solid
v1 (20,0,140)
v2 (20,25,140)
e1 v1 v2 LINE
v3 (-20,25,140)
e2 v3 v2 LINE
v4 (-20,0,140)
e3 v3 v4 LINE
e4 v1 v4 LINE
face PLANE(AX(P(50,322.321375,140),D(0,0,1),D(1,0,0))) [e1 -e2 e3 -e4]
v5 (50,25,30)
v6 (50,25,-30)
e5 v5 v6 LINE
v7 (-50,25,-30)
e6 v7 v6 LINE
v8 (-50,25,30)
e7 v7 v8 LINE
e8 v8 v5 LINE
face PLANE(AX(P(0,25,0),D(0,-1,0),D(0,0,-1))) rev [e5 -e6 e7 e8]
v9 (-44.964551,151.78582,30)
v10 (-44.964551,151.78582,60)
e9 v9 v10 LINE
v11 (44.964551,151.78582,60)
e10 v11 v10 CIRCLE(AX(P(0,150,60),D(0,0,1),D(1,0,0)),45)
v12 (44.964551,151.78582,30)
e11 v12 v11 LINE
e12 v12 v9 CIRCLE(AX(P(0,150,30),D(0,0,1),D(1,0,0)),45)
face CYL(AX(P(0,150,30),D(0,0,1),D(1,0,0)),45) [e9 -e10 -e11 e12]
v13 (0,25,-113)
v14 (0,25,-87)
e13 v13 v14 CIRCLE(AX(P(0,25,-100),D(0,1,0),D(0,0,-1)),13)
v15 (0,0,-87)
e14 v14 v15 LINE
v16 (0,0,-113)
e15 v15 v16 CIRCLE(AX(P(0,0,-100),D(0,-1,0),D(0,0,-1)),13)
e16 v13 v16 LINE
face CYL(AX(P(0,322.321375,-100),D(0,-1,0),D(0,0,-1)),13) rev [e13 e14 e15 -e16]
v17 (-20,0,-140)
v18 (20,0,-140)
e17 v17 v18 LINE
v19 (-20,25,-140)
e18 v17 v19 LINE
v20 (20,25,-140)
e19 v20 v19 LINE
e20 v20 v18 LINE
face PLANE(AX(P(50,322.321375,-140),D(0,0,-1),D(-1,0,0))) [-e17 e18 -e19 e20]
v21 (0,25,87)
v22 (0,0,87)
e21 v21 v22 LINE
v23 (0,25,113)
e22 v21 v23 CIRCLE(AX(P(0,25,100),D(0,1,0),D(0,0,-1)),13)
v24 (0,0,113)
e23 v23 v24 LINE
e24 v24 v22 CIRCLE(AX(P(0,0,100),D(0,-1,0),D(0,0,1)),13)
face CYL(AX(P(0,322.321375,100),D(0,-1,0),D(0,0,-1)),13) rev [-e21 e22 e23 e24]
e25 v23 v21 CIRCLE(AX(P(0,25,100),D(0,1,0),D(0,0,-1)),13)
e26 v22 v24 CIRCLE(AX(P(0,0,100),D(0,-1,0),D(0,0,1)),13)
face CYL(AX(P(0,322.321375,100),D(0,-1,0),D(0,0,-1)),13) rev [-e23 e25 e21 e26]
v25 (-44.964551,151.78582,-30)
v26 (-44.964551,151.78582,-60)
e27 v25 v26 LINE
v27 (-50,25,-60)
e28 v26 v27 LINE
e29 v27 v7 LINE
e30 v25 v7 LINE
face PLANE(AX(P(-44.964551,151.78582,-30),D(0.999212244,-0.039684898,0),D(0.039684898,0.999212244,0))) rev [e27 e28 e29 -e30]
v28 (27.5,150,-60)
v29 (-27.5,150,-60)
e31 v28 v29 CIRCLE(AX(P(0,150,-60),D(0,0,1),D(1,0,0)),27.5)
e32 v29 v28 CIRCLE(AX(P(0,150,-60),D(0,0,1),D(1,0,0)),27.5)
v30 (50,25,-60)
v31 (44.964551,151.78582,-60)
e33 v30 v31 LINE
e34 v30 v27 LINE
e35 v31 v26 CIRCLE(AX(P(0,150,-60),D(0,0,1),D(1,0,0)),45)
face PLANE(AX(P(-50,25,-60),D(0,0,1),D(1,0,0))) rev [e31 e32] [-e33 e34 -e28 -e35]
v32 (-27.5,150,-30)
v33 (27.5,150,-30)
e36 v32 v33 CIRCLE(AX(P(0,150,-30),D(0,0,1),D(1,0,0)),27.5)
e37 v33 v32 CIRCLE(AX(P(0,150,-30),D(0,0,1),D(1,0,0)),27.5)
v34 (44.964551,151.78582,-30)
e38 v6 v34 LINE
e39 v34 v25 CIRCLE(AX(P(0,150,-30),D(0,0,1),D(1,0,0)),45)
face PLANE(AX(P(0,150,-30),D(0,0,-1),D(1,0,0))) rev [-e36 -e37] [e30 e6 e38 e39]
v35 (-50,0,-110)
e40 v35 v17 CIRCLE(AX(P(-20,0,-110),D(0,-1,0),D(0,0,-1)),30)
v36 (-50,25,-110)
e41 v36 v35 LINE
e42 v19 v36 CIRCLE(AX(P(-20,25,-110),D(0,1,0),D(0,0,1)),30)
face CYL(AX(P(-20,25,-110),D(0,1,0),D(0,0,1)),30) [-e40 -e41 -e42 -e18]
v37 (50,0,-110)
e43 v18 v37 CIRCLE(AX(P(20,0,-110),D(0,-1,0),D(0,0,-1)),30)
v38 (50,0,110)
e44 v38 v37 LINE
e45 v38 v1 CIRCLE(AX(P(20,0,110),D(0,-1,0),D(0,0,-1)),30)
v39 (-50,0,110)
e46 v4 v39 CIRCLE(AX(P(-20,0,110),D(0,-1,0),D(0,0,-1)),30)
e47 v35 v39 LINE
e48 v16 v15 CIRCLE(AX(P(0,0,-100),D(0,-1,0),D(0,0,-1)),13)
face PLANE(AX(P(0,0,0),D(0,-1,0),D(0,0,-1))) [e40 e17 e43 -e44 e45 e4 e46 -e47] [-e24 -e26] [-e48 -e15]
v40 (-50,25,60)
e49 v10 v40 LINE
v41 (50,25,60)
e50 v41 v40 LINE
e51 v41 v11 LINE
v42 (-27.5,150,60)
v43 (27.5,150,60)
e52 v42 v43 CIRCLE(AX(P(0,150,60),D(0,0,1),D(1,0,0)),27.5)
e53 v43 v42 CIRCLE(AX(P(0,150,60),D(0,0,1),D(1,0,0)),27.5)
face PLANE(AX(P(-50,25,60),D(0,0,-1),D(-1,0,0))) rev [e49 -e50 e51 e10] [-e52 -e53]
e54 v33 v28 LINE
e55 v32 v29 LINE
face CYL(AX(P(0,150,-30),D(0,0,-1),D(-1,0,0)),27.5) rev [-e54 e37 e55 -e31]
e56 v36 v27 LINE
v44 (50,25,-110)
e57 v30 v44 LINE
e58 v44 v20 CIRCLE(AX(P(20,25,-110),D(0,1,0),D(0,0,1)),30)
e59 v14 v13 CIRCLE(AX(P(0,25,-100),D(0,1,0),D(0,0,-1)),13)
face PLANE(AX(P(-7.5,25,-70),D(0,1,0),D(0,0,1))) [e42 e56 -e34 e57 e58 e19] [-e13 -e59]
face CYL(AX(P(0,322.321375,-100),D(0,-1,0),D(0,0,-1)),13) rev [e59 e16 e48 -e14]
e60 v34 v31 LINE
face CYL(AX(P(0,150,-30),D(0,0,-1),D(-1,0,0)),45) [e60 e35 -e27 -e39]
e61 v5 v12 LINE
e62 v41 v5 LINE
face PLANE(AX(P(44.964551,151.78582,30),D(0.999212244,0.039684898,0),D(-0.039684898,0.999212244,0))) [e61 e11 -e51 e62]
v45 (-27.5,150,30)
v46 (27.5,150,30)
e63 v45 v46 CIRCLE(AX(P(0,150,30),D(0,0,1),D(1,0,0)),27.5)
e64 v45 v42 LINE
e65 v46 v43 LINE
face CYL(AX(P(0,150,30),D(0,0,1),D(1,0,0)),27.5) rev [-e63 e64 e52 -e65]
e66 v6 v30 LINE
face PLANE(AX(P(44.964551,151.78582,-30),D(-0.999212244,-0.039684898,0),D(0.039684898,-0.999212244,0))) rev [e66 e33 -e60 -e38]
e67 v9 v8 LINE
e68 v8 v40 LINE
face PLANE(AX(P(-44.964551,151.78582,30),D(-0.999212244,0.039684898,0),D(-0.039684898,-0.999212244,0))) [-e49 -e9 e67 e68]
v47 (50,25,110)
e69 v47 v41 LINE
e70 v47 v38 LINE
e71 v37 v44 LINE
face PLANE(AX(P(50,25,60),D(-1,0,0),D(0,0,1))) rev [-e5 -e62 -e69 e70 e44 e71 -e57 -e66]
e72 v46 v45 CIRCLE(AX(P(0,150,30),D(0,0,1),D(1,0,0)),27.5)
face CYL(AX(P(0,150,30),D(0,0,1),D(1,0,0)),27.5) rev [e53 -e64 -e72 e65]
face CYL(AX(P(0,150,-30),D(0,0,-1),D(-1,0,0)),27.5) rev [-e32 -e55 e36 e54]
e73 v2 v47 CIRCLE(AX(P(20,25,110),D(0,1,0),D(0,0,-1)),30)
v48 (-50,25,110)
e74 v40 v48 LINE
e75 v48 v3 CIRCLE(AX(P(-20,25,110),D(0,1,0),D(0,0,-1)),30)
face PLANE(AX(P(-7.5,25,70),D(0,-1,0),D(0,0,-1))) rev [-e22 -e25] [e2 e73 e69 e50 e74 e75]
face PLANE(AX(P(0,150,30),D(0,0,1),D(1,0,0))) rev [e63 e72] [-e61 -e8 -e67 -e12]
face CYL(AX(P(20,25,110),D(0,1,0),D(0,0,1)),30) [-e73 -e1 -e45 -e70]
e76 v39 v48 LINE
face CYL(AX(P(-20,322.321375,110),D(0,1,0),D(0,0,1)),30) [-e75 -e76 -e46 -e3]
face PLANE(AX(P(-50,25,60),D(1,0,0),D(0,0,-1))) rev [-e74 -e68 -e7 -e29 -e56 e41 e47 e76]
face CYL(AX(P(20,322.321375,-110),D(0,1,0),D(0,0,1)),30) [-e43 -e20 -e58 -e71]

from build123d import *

# Parameters (mm, degrees)
SKETCH_1_W           = 100
SKETCH_1_H           = 120
BOSS_EXTRUDE_1_DEPTH = 25
SKETCH_2_R           = 27.5
BOSS_EXTRUDE_2_DEPTH = 30
SKETCH_4_W           = 15
SKETCH_4_H           = 25
BOSS_EXTRUDE_3_DEPTH = 10
SKETCH_5_W           = 100
SKETCH_5_H           = 280
SKETCH_5_R           = 13
BOSS_EXTRUDE_4_DEPTH = 25
FILLET_1_R           = 30


with BuildPart() as part:
    # Sketch 1 → Boss-Extrude 1 (new body)
    with BuildSketch(Plane(origin=(0, 0, 0), x_dir=(1, 0, 0), z_dir=(0, 1, 0))):
        Rectangle(SKETCH_1_W, SKETCH_1_H)
    extrude(amount=BOSS_EXTRUDE_1_DEPTH)

    # Sketch 2 → Boss-Extrude 2 (add)
    with BuildSketch(Plane.XY.offset(60)):
        with BuildLine():
            Line((-44.964550988, 151.785820395), (-50, 25))
            Line((-50, 25), (50, 25))
            Line((50, 25), (44.964550988, 151.785820395))
            ThreePointArc((44.964550988, 151.785820395), (0, 195), (-44.964550988, 151.785820395))
        make_face()
        with Locations((0, 150)):
            Circle(SKETCH_2_R, mode=Mode.SUBTRACT)
    boss_extrude_2 = extrude(amount=-BOSS_EXTRUDE_2_DEPTH)

    # Sketch 4 → Boss-Extrude 3 (add)
    with BuildSketch(Plane.XY.offset(60)):
        with Locations((0, 12.5)):
            Rectangle(SKETCH_4_W, SKETCH_4_H)
    boss_extrude_3 = extrude(amount=BOSS_EXTRUDE_3_DEPTH)

    # Mirror 1: Boss-Extrude 2, Boss-Extrude 3 across plane
    add(boss_extrude_2.mirror(Plane.XY))
    add(boss_extrude_3.mirror(Plane.XY))

    # Sketch 5 → Boss-Extrude 4 (add)
    with BuildSketch(Plane.XZ):
        Rectangle(SKETCH_5_W, SKETCH_5_H)
        with Locations(Location((0, -100, 0), (0, 0, 270))):
            Circle(SKETCH_5_R, mode=Mode.SUBTRACT)
        with Locations(Location((0, 100, 0), (0, 0, 270))):
            Circle(SKETCH_5_R, mode=Mode.SUBTRACT)
    extrude(amount=-BOSS_EXTRUDE_4_DEPTH)

    # Fillet 1
    fillet_1_edges = [part.edges().sort_by_distance(p)[0] for p in [
        (-50, 12.5, -140),
        (50, 12.5, 140),
        (50, 12.5, -140),
        (-50, 12.5, 140),
    ]]
    fillet(fillet_1_edges, radius=FILLET_1_R)


solid = part.part
